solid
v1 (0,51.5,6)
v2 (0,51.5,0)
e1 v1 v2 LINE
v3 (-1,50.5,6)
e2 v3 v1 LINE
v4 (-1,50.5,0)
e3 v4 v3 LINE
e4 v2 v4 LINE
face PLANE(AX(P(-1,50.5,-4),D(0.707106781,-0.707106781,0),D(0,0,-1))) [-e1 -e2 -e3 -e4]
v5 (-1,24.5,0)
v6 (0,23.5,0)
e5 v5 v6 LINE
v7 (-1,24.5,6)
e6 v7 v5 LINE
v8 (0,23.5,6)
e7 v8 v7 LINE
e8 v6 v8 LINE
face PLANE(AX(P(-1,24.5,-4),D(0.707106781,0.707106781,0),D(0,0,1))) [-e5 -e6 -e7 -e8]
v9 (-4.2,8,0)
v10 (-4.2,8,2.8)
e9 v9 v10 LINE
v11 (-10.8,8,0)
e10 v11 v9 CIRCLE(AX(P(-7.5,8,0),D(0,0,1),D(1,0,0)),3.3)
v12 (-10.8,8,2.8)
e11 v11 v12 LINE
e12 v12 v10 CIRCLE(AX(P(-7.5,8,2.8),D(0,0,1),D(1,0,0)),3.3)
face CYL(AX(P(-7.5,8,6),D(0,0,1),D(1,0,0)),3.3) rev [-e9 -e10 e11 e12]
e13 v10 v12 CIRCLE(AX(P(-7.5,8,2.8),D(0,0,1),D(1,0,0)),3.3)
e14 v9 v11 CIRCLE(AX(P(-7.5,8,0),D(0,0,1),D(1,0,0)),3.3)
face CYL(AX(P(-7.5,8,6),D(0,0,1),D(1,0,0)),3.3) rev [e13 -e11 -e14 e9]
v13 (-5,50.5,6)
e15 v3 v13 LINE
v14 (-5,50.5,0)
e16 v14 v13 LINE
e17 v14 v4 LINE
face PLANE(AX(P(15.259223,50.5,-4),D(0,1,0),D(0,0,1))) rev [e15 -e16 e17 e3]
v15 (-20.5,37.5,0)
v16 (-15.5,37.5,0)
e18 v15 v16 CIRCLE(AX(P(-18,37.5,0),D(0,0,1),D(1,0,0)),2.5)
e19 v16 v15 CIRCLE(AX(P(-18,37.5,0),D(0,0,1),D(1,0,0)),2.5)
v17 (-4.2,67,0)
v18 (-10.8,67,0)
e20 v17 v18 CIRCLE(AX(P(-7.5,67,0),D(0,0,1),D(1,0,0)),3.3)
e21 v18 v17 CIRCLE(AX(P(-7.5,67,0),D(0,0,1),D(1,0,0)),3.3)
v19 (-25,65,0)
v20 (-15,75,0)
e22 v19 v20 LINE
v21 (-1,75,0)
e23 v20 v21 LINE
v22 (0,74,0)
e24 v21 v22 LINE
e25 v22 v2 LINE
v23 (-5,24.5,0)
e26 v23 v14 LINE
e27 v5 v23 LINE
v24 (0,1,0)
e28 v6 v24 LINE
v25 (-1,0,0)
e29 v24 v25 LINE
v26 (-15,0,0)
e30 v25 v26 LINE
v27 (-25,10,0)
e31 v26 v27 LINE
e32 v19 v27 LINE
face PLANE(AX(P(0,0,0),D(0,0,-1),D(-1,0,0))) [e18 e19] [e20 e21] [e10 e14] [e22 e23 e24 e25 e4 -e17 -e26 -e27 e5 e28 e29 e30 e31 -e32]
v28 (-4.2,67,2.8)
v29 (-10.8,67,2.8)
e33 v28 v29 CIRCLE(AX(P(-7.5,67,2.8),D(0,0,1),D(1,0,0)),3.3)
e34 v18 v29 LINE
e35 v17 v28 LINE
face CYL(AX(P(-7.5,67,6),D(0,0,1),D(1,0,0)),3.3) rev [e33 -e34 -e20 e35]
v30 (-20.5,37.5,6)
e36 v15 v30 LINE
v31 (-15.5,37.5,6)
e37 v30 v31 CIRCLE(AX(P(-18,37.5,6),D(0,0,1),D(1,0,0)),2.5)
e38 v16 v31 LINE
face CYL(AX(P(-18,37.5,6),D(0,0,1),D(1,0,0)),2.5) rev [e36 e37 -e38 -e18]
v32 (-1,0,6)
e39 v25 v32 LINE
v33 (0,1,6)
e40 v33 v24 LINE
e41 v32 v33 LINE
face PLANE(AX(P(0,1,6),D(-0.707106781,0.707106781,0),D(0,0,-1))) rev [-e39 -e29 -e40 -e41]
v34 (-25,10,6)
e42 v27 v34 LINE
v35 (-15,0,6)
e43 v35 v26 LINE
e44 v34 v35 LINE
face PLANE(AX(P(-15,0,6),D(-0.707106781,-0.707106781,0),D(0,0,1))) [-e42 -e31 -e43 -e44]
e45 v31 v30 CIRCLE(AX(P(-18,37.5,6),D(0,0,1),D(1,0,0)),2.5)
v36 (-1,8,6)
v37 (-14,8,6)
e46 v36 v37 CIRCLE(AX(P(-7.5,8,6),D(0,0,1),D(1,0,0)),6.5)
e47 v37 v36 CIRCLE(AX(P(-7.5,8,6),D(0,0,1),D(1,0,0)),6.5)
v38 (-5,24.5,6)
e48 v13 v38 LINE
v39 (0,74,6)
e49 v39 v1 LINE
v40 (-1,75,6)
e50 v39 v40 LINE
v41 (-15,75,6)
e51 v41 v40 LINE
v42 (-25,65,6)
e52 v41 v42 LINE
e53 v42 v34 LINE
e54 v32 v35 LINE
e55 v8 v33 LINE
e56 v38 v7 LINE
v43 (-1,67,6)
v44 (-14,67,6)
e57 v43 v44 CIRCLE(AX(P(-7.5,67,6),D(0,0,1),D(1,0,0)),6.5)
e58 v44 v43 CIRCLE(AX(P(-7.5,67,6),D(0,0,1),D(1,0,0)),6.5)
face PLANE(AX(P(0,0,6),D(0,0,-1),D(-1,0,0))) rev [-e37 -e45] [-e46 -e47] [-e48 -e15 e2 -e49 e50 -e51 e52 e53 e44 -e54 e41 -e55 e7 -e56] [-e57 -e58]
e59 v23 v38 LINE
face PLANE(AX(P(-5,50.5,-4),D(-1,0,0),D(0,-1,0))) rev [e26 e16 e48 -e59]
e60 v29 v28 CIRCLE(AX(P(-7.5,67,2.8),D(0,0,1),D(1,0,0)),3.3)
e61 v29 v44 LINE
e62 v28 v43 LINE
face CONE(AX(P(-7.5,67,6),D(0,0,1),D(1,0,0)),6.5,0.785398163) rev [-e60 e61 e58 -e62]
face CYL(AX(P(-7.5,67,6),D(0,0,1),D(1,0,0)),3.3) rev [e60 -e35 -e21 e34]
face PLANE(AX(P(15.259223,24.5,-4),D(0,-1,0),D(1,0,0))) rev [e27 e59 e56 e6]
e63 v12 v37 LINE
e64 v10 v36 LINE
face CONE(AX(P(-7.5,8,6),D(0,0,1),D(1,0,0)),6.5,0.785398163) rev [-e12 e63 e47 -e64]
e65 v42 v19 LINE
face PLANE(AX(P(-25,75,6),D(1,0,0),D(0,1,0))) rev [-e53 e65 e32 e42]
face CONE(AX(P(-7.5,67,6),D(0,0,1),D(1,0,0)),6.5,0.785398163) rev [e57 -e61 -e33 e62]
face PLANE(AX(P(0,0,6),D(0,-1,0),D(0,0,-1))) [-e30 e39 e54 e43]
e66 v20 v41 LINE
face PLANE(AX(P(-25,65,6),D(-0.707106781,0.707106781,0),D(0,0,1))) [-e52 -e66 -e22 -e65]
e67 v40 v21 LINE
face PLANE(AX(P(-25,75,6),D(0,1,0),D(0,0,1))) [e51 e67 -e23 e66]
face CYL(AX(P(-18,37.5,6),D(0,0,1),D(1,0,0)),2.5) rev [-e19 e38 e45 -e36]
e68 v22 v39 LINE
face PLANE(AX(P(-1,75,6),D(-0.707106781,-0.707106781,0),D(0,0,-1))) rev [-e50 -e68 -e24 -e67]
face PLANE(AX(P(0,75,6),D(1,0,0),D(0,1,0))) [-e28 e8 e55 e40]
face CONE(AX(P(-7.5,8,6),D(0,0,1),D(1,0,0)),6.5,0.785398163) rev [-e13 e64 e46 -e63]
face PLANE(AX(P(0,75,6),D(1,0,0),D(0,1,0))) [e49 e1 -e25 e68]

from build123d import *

# Parameters (mm, degrees)
SKETCH1_W                                   = 25
SKETCH1_H                                   = 75
EXTRUDE_THIN1_DEPTH                         = 6
CHAMFER1_SIZE                               = 1
HOLE_SIZE_PER_SOCKET_FLAT_COUNTEBLZ_2_COUNT = 2
HOLE_SIZE_PER_SOCKET_FLAT_COUNTEBLZ_2_PITCH = 59
CHAMFER2_SIZE                               = 10
M6_TAPPED_HOLE1_D                           = 5
SKETCH12_W                                  = 20.259222761
SKETCH12_H                                  = 26
CUT_EXTRUDE1_DEPTH                          = 10
CHAMFER3_SIZE                               = 1


with BuildPart() as part:
    # Sketch1 → Extrude-Thin1 (new body)
    with BuildSketch(Plane.XY):
        with Locations((-12.5, 37.5)):
            Rectangle(SKETCH1_W, SKETCH1_H)
    extrude(amount=EXTRUDE_THIN1_DEPTH)

    # Chamfer1
    chamfer1_edges = [part.edges().sort_by_distance(p)[0] for p in [
        (0, 75, 3),
        (0, 0, 3),
    ]]
    chamfer(chamfer1_edges, length=CHAMFER1_SIZE)

    # Sketch9 → Hole size (per socket flat counteBLZKk head screw type)1 (revolve, cut)
    with BuildSketch(Plane(origin=(-7.5, 67, 6), x_dir=(0, -1, 0), z_dir=(1, 0, 0))):
        Polygon((0, 0), (0, 6), (3.3, 6), (3.3, 3.2), (6.5, 0), align=None)
    hole_size_per_socket_flat_counteblzkk_h = revolve(axis=Axis((-7.5, 67, 12.35), (0, 0, -1)), mode=Mode.SUBTRACT)

    # Hole size _per socket flat counteBLZ 2: Hole size (per socket flat counteBLZKk head screw type)1 ×2
    with Locations(*[(0, -i * HOLE_SIZE_PER_SOCKET_FLAT_COUNTEBLZ_2_PITCH, 0) for i in range(1, HOLE_SIZE_PER_SOCKET_FLAT_COUNTEBLZ_2_COUNT)]):
        add(hole_size_per_socket_flat_counteblzkk_h, mode=Mode.SUBTRACT)

    # Chamfer2
    chamfer2_edges = [part.edges().sort_by_distance(p)[0] for p in [
        (-25, 75, 3),
        (-25, 0, 3),
    ]]
    chamfer(chamfer2_edges, length=CHAMFER2_SIZE)

    # M6 Tapped Hole1 (through all)
    with Locations(Plane.XY.offset(6)):
        with Locations((-18, 37.5)):
            Hole(M6_TAPPED_HOLE1_D / 2)

    # Sketch12 → Cut-Extrude1 (cut)
    with BuildSketch(Plane.XY.offset(6)):
        with Locations((5.129611381, 37.5)):
            Rectangle(SKETCH12_W, SKETCH12_H)
    extrude(amount=-CUT_EXTRUDE1_DEPTH, mode=Mode.SUBTRACT)

    # Chamfer3
    chamfer3_edges = [part.edges().sort_by_distance(p)[0] for p in [
        (0, 50.5, 3),
        (0, 24.5, 3),
    ]]
    chamfer(chamfer3_edges, length=CHAMFER3_SIZE)


solid = part.part
